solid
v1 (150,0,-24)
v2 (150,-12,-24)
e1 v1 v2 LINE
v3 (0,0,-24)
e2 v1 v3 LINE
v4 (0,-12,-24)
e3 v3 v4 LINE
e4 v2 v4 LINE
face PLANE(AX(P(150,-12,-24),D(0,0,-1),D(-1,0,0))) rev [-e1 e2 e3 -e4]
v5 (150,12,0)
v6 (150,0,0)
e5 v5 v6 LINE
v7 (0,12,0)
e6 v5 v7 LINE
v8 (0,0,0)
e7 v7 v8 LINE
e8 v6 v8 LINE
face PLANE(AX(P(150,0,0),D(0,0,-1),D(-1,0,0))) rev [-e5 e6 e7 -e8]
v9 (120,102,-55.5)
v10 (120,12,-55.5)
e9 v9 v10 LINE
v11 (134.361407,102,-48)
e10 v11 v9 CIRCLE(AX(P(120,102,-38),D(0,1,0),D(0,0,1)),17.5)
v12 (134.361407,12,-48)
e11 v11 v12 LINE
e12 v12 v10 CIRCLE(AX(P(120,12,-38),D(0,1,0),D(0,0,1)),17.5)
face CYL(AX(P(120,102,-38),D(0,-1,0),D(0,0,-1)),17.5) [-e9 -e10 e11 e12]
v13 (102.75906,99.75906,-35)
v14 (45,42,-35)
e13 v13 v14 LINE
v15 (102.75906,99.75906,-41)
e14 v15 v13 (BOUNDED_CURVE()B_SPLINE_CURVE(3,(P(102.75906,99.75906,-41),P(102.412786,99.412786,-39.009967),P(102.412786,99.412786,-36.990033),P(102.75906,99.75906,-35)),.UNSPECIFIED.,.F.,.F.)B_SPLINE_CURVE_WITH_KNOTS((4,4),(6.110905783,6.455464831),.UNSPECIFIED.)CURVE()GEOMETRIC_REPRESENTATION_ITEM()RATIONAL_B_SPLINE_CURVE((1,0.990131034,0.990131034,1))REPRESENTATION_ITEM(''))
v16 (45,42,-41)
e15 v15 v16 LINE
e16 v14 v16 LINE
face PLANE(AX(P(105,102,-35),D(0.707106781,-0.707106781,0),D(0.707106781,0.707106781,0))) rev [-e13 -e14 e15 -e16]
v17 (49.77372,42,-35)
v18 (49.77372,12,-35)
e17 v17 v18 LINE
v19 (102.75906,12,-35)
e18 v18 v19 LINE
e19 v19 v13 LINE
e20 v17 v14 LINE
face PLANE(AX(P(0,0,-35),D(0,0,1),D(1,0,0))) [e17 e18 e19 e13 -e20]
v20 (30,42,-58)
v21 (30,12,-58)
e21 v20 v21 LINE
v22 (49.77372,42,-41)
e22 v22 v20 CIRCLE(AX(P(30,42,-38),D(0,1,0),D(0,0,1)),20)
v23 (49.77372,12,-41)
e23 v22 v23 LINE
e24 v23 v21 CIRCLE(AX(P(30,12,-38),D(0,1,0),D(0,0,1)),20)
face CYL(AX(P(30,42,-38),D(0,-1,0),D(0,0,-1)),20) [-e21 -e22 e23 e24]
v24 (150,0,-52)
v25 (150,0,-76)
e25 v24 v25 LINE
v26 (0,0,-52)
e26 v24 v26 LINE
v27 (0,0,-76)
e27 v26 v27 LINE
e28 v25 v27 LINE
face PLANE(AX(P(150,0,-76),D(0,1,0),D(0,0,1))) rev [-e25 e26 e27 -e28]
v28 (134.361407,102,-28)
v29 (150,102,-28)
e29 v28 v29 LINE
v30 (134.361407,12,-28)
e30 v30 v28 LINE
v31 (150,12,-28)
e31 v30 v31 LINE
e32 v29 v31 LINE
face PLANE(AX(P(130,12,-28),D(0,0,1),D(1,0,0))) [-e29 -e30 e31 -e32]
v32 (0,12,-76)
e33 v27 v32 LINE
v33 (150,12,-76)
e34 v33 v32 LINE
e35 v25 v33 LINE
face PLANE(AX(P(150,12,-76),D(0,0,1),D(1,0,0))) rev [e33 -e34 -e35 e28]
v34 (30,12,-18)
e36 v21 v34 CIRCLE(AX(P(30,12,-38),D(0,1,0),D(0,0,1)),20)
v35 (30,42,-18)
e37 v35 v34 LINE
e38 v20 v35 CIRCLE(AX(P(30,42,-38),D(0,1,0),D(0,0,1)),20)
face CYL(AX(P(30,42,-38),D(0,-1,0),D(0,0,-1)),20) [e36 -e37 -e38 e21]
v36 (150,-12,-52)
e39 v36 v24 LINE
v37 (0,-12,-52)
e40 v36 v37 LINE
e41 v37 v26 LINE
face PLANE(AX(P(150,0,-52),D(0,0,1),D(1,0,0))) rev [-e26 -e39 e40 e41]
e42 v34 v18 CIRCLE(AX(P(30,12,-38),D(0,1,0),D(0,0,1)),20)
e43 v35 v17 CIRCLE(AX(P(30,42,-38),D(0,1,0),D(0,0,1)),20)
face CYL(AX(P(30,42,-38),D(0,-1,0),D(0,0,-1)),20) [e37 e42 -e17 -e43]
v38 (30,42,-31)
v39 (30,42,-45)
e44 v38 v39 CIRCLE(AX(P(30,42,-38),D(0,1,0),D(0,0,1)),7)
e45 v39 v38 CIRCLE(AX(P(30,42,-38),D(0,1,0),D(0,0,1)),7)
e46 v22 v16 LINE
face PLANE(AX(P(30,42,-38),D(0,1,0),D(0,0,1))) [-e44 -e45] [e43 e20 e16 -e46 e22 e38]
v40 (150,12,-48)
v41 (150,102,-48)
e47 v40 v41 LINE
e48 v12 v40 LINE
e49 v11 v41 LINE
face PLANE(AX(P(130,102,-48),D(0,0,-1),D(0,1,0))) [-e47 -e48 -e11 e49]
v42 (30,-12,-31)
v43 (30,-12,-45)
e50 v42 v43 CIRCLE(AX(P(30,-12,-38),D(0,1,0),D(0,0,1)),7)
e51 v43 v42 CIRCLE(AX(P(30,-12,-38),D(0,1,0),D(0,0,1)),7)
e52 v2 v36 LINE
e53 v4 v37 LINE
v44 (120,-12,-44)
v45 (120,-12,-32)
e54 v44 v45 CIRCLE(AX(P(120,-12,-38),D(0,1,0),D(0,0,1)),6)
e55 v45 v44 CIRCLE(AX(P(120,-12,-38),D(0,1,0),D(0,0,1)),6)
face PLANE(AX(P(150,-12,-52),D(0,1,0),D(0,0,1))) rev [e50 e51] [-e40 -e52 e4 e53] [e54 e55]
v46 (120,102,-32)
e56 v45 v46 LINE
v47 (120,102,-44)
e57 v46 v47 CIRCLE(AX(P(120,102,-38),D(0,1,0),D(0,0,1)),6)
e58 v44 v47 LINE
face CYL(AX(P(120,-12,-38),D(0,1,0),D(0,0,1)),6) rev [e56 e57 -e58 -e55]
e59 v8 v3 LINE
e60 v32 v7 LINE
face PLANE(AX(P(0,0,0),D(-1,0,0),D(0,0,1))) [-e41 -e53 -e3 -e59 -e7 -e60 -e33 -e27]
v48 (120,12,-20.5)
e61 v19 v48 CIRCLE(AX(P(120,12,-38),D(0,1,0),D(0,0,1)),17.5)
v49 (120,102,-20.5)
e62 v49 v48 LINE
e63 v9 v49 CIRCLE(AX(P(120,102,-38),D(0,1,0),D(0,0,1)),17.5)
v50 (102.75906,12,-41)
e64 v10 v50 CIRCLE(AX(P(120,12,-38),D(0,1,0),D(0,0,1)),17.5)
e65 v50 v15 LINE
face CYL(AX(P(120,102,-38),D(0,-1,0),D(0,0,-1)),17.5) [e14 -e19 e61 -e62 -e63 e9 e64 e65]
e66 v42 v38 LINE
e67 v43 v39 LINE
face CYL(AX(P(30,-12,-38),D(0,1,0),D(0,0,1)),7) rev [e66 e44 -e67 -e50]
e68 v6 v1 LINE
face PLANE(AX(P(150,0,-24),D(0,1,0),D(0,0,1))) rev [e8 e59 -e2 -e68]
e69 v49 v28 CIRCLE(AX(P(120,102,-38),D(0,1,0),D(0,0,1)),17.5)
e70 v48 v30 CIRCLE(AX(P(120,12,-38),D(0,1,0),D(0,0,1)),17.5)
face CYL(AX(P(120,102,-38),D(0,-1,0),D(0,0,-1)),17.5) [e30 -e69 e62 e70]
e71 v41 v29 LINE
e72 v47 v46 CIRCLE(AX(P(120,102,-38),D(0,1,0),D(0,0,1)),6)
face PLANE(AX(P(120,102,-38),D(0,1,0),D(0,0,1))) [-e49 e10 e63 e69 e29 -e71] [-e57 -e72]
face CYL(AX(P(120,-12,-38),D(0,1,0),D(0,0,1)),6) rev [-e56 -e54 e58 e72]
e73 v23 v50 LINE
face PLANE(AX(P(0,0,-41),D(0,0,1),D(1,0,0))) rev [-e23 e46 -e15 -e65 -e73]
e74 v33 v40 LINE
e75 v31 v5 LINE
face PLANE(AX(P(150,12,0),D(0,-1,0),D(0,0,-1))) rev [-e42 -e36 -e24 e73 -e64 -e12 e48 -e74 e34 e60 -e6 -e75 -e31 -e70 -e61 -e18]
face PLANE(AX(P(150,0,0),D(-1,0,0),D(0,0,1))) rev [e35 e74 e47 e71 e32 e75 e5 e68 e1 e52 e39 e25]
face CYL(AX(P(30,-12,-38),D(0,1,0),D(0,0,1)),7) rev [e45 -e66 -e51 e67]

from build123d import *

# Parameters (mm, degrees)
BASE_PLATE_DEPTH          = 150
WEB_RIB_DEPTH             = 3
TALL_BOSS_PROFILE_R       = 17.5
TALL_BOSS_35_DEPTH        = 90
TALL_BOSS_BORE_PROFILE_R  = 6
TALL_BOSS_BORE_12_DEPTH   = 204.155113152
SHORT_BOSS_PROFILE_R      = 20
SHORT_BOSS_40_DEPTH       = 30
SHORT_BOSS_BORE_PROFILE_R = 7
SHORT_BOSS_BORE_14_DEPTH  = 179.538511252
SIDE_LUG_DEPTH            = 20


with BuildPart() as part:
    # Base Plate Profile → Base Plate (new body)
    with BuildSketch(Plane(origin=(0, 0, 0), x_dir=(0, 0, -1), z_dir=(1, 0, 0))):
        Polygon((0, 0), (0, 12), (76, 12), (76, 0), (52, 0), (52, -12), (24, -12), (24, 0), align=None)
    extrude(amount=BASE_PLATE_DEPTH)

    # Web Rib Profile → Web Rib (add, symmetric)
    with BuildSketch(Plane.XY.offset(-38)):
        Polygon((75, 12), (105, 12), (105, 102), (45, 42), (45, 12), align=None)
    extrude(amount=WEB_RIB_DEPTH, both=True)

    # Tall Boss Profile → Tall Boss Ø35 (add)
    with BuildSketch(Plane(origin=(0, 12, 0), x_dir=(1, 0, 0), z_dir=(0, 1, 0))):
        with Locations(Location((120, 38, 0), (0, 0, 170.129110394))):
            Circle(TALL_BOSS_PROFILE_R)
    extrude(amount=TALL_BOSS_35_DEPTH)

    # Tall Boss Bore Profile → Tall Boss Bore Ø12 (cut, through all)
    with BuildSketch(Plane(origin=(0, 102, 0), x_dir=(1, 0, 0), z_dir=(0, 1, 0))):
        with Locations(Location((120, 38, 0), (0, 0, 270))):
            Circle(TALL_BOSS_BORE_PROFILE_R)
    extrude(amount=-TALL_BOSS_BORE_12_DEPTH, mode=Mode.SUBTRACT)

    # Short Boss Profile → Short Boss Ø40 (add)
    with BuildSketch(Plane(origin=(0, 12, 0), x_dir=(1, 0, 0), z_dir=(0, 1, 0))):
        with Locations((30, 38)):
            Circle(SHORT_BOSS_PROFILE_R)
    extrude(amount=SHORT_BOSS_40_DEPTH)

    # Short Boss Bore Profile → Short Boss Bore Ø14 (cut, through all)
    with BuildSketch(Plane(origin=(0, 42, 0), x_dir=(1, 0, 0), z_dir=(0, 1, 0))):
        with Locations(Location((30, 38, 0), (0, 0, 270))):
            Circle(SHORT_BOSS_BORE_PROFILE_R)
    extrude(amount=-SHORT_BOSS_BORE_14_DEPTH, mode=Mode.SUBTRACT)

    # Side Lug Profile → Side Lug (add)
    with BuildSketch(Plane(origin=(150, 0, 0), x_dir=(0, 0, -1), z_dir=(1, 0, 0))):
        Polygon((38, 12), (28, 12), (28, 102), (48, 102), (48, 12), align=None)
    extrude(amount=-SIDE_LUG_DEPTH)


solid = part.part
